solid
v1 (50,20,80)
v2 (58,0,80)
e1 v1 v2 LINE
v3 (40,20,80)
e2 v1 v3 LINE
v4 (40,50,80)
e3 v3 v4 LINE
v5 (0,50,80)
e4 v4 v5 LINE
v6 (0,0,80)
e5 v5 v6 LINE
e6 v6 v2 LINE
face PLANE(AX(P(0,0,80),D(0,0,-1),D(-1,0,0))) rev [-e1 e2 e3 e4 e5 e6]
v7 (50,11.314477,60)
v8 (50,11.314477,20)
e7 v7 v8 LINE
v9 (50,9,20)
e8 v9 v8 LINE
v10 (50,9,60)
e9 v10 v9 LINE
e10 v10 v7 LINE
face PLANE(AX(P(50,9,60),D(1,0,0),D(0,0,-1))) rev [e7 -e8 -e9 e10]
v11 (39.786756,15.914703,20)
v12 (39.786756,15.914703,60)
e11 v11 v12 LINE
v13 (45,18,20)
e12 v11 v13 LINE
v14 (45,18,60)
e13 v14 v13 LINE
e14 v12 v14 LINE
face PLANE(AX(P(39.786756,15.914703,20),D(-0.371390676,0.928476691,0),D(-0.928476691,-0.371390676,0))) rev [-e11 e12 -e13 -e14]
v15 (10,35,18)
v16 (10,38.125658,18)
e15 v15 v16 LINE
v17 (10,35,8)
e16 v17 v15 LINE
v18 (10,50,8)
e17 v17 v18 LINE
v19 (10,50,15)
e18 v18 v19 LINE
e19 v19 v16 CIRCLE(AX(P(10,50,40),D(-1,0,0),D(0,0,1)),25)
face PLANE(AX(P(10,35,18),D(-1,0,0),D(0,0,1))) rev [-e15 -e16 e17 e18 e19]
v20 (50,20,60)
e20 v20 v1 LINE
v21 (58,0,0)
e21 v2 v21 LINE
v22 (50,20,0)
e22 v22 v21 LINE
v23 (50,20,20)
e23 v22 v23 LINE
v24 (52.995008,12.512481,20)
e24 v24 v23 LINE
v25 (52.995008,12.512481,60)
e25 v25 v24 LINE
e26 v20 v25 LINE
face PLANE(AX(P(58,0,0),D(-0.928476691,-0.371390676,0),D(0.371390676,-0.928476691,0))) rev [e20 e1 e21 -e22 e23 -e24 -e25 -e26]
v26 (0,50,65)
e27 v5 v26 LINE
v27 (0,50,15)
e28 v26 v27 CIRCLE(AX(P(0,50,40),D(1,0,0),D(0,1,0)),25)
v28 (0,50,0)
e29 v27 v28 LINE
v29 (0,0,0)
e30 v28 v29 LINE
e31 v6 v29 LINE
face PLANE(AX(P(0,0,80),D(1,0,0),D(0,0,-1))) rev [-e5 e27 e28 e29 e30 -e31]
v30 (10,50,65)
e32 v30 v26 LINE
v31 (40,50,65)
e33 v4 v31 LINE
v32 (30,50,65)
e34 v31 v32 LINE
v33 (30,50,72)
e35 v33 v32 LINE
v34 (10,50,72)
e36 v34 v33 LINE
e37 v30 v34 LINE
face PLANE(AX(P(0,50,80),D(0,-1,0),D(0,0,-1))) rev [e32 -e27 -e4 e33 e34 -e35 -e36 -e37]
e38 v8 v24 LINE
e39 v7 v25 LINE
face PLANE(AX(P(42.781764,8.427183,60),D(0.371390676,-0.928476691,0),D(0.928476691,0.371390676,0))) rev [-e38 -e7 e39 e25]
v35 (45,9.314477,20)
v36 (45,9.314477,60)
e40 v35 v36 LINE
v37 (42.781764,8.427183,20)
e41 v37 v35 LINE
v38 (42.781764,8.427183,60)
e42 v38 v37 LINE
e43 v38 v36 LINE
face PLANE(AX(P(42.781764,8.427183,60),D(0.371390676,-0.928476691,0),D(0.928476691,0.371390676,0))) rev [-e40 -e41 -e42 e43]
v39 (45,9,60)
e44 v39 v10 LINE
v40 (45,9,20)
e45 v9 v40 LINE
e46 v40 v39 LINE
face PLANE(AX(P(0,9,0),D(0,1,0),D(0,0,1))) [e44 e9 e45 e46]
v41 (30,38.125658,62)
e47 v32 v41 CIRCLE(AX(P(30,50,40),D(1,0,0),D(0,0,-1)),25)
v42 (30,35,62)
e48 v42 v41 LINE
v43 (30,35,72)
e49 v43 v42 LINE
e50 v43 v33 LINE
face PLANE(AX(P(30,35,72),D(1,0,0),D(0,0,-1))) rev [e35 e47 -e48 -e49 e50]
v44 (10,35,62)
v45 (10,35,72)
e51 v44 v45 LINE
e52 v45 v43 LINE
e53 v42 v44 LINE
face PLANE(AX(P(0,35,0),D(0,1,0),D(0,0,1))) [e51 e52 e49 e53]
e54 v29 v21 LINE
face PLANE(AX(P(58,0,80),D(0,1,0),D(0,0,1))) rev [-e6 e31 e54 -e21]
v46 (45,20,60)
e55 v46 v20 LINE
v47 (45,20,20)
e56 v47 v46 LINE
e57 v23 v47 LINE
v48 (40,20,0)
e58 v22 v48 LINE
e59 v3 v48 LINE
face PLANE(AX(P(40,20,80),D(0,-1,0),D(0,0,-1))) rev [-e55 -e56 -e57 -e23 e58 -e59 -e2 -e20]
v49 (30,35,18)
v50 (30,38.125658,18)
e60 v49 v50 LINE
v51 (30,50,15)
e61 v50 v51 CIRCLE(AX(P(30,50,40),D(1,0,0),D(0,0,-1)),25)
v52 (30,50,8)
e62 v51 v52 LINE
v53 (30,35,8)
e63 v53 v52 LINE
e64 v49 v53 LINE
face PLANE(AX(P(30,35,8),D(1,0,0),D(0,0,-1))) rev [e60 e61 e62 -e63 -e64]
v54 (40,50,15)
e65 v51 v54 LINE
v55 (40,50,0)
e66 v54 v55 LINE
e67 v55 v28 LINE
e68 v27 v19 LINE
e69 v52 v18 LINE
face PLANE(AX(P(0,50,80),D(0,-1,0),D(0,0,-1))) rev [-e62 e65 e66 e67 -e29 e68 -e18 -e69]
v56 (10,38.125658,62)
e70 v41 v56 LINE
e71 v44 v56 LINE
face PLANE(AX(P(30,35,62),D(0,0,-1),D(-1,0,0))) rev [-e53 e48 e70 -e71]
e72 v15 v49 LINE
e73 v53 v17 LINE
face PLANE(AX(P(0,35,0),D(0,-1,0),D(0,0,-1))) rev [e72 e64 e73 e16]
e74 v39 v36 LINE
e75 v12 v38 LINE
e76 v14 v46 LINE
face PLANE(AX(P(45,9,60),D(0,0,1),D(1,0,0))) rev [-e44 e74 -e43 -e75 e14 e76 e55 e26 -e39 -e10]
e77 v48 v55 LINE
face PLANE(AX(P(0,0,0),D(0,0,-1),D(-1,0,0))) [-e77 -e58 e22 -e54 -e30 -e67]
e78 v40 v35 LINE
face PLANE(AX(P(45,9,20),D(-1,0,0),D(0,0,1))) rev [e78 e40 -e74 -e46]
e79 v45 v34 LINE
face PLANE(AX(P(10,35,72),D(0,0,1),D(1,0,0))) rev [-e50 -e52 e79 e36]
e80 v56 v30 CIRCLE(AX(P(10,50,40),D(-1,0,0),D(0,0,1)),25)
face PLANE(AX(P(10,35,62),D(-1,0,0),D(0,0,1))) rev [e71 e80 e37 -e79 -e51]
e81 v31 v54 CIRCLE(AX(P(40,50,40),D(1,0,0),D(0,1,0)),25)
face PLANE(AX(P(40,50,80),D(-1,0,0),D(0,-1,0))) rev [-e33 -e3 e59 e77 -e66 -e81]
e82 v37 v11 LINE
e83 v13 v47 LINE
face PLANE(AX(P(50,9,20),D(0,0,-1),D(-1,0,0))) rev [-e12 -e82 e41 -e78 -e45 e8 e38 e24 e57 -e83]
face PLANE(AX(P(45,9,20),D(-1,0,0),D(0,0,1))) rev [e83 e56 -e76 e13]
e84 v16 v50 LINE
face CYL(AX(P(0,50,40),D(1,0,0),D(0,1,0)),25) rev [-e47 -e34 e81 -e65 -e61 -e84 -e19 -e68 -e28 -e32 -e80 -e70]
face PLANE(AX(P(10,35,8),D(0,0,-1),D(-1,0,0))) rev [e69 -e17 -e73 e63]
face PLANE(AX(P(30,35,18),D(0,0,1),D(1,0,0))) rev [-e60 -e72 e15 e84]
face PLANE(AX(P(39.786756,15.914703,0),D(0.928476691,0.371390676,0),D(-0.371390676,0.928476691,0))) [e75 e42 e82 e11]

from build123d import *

# Parameters (mm, degrees)
BASE_BLOCK_DEPTH             = 80
UPRIGHT_NOTCHES_SKETCH_W     = 20
UPRIGHT_NOTCHES_SKETCH_H     = 10
UPRIGHT_TOP_NOTCHES_DEPTH    = 15
SADDLE_BORE_SKETCH_R         = 25
SADDLE_BORE_50_DEPTH         = 103.46950766
FRONT_SLOPE_CUT_DEPTH        = 111.742945599
FRONT_SLOT_SKETCH_W          = 5
FRONT_SLOT_SKETCH_H          = 40
FRONT_SLOT_40X5_DEPTH        = 11
FRONT_SLOT_UNDERCUT_SKETCH_W = 40
FRONT_SLOT_UNDERCUT_SKETCH_H = 8.064305279
FRONT_SLOT_UNDERCUT_DEPTH    = 11


with BuildPart() as part:
    # Base Profile Sketch → Base Block (new body)
    with BuildSketch(Plane.XY):
        Polygon((0, 0), (0, 50), (40, 50), (40, 20), (58, 20), (58, 0), align=None)
    extrude(amount=BASE_BLOCK_DEPTH)

    # Upright Notches Sketch → Upright Top Notches (cut)
    with BuildSketch(Plane(origin=(0, 50, 0), x_dir=(1, 0, 0), z_dir=(0, 1, 0))):
        with Locations((20, -13)):
            Rectangle(UPRIGHT_NOTCHES_SKETCH_W, UPRIGHT_NOTCHES_SKETCH_H)
        with Locations((20, -67)):
            Rectangle(UPRIGHT_NOTCHES_SKETCH_W, UPRIGHT_NOTCHES_SKETCH_H)
    extrude(amount=-UPRIGHT_TOP_NOTCHES_DEPTH, mode=Mode.SUBTRACT)

    # Saddle Bore Sketch → Saddle Bore Ø50 (cut, through all)
    with BuildSketch(Plane(origin=(40, 0, 0), x_dir=(0, 0, -1), z_dir=(1, 0, 0))):
        with Locations((-40, 50)):
            Circle(SADDLE_BORE_SKETCH_R)
    extrude(amount=-SADDLE_BORE_50_DEPTH, mode=Mode.SUBTRACT)

    # Front Slope Sketch → Front Slope Cut (cut, through all)
    with BuildSketch(Plane.XY.offset(80)):
        Polygon((50, 20), (58, 20), (58, 0), align=None)
    extrude(amount=-FRONT_SLOPE_CUT_DEPTH, mode=Mode.SUBTRACT)

    # Front Slot Sketch → Front Slot 40x5 (cut)
    with BuildSketch(Plane(origin=(0, 20, 0), x_dir=(1, 0, 0), z_dir=(0, 1, 0))):
        with Locations((47.5, -40)):
            Rectangle(FRONT_SLOT_SKETCH_W, FRONT_SLOT_SKETCH_H)
    extrude(amount=-FRONT_SLOT_40X5_DEPTH, mode=Mode.SUBTRACT)

    # Front Slot Undercut Sketch → Front Slot Undercut (cut)
    with BuildSketch(Plane(origin=(50, 20, 0), x_dir=(0, 0, -1), z_dir=(0.9284766908852593, 0.3713906763541041, 0))):
        with Locations((-40, -4.03215264)):
            Rectangle(FRONT_SLOT_UNDERCUT_SKETCH_W, FRONT_SLOT_UNDERCUT_SKETCH_H)
    extrude(amount=-FRONT_SLOT_UNDERCUT_DEPTH, mode=Mode.SUBTRACT)


solid = part.part
